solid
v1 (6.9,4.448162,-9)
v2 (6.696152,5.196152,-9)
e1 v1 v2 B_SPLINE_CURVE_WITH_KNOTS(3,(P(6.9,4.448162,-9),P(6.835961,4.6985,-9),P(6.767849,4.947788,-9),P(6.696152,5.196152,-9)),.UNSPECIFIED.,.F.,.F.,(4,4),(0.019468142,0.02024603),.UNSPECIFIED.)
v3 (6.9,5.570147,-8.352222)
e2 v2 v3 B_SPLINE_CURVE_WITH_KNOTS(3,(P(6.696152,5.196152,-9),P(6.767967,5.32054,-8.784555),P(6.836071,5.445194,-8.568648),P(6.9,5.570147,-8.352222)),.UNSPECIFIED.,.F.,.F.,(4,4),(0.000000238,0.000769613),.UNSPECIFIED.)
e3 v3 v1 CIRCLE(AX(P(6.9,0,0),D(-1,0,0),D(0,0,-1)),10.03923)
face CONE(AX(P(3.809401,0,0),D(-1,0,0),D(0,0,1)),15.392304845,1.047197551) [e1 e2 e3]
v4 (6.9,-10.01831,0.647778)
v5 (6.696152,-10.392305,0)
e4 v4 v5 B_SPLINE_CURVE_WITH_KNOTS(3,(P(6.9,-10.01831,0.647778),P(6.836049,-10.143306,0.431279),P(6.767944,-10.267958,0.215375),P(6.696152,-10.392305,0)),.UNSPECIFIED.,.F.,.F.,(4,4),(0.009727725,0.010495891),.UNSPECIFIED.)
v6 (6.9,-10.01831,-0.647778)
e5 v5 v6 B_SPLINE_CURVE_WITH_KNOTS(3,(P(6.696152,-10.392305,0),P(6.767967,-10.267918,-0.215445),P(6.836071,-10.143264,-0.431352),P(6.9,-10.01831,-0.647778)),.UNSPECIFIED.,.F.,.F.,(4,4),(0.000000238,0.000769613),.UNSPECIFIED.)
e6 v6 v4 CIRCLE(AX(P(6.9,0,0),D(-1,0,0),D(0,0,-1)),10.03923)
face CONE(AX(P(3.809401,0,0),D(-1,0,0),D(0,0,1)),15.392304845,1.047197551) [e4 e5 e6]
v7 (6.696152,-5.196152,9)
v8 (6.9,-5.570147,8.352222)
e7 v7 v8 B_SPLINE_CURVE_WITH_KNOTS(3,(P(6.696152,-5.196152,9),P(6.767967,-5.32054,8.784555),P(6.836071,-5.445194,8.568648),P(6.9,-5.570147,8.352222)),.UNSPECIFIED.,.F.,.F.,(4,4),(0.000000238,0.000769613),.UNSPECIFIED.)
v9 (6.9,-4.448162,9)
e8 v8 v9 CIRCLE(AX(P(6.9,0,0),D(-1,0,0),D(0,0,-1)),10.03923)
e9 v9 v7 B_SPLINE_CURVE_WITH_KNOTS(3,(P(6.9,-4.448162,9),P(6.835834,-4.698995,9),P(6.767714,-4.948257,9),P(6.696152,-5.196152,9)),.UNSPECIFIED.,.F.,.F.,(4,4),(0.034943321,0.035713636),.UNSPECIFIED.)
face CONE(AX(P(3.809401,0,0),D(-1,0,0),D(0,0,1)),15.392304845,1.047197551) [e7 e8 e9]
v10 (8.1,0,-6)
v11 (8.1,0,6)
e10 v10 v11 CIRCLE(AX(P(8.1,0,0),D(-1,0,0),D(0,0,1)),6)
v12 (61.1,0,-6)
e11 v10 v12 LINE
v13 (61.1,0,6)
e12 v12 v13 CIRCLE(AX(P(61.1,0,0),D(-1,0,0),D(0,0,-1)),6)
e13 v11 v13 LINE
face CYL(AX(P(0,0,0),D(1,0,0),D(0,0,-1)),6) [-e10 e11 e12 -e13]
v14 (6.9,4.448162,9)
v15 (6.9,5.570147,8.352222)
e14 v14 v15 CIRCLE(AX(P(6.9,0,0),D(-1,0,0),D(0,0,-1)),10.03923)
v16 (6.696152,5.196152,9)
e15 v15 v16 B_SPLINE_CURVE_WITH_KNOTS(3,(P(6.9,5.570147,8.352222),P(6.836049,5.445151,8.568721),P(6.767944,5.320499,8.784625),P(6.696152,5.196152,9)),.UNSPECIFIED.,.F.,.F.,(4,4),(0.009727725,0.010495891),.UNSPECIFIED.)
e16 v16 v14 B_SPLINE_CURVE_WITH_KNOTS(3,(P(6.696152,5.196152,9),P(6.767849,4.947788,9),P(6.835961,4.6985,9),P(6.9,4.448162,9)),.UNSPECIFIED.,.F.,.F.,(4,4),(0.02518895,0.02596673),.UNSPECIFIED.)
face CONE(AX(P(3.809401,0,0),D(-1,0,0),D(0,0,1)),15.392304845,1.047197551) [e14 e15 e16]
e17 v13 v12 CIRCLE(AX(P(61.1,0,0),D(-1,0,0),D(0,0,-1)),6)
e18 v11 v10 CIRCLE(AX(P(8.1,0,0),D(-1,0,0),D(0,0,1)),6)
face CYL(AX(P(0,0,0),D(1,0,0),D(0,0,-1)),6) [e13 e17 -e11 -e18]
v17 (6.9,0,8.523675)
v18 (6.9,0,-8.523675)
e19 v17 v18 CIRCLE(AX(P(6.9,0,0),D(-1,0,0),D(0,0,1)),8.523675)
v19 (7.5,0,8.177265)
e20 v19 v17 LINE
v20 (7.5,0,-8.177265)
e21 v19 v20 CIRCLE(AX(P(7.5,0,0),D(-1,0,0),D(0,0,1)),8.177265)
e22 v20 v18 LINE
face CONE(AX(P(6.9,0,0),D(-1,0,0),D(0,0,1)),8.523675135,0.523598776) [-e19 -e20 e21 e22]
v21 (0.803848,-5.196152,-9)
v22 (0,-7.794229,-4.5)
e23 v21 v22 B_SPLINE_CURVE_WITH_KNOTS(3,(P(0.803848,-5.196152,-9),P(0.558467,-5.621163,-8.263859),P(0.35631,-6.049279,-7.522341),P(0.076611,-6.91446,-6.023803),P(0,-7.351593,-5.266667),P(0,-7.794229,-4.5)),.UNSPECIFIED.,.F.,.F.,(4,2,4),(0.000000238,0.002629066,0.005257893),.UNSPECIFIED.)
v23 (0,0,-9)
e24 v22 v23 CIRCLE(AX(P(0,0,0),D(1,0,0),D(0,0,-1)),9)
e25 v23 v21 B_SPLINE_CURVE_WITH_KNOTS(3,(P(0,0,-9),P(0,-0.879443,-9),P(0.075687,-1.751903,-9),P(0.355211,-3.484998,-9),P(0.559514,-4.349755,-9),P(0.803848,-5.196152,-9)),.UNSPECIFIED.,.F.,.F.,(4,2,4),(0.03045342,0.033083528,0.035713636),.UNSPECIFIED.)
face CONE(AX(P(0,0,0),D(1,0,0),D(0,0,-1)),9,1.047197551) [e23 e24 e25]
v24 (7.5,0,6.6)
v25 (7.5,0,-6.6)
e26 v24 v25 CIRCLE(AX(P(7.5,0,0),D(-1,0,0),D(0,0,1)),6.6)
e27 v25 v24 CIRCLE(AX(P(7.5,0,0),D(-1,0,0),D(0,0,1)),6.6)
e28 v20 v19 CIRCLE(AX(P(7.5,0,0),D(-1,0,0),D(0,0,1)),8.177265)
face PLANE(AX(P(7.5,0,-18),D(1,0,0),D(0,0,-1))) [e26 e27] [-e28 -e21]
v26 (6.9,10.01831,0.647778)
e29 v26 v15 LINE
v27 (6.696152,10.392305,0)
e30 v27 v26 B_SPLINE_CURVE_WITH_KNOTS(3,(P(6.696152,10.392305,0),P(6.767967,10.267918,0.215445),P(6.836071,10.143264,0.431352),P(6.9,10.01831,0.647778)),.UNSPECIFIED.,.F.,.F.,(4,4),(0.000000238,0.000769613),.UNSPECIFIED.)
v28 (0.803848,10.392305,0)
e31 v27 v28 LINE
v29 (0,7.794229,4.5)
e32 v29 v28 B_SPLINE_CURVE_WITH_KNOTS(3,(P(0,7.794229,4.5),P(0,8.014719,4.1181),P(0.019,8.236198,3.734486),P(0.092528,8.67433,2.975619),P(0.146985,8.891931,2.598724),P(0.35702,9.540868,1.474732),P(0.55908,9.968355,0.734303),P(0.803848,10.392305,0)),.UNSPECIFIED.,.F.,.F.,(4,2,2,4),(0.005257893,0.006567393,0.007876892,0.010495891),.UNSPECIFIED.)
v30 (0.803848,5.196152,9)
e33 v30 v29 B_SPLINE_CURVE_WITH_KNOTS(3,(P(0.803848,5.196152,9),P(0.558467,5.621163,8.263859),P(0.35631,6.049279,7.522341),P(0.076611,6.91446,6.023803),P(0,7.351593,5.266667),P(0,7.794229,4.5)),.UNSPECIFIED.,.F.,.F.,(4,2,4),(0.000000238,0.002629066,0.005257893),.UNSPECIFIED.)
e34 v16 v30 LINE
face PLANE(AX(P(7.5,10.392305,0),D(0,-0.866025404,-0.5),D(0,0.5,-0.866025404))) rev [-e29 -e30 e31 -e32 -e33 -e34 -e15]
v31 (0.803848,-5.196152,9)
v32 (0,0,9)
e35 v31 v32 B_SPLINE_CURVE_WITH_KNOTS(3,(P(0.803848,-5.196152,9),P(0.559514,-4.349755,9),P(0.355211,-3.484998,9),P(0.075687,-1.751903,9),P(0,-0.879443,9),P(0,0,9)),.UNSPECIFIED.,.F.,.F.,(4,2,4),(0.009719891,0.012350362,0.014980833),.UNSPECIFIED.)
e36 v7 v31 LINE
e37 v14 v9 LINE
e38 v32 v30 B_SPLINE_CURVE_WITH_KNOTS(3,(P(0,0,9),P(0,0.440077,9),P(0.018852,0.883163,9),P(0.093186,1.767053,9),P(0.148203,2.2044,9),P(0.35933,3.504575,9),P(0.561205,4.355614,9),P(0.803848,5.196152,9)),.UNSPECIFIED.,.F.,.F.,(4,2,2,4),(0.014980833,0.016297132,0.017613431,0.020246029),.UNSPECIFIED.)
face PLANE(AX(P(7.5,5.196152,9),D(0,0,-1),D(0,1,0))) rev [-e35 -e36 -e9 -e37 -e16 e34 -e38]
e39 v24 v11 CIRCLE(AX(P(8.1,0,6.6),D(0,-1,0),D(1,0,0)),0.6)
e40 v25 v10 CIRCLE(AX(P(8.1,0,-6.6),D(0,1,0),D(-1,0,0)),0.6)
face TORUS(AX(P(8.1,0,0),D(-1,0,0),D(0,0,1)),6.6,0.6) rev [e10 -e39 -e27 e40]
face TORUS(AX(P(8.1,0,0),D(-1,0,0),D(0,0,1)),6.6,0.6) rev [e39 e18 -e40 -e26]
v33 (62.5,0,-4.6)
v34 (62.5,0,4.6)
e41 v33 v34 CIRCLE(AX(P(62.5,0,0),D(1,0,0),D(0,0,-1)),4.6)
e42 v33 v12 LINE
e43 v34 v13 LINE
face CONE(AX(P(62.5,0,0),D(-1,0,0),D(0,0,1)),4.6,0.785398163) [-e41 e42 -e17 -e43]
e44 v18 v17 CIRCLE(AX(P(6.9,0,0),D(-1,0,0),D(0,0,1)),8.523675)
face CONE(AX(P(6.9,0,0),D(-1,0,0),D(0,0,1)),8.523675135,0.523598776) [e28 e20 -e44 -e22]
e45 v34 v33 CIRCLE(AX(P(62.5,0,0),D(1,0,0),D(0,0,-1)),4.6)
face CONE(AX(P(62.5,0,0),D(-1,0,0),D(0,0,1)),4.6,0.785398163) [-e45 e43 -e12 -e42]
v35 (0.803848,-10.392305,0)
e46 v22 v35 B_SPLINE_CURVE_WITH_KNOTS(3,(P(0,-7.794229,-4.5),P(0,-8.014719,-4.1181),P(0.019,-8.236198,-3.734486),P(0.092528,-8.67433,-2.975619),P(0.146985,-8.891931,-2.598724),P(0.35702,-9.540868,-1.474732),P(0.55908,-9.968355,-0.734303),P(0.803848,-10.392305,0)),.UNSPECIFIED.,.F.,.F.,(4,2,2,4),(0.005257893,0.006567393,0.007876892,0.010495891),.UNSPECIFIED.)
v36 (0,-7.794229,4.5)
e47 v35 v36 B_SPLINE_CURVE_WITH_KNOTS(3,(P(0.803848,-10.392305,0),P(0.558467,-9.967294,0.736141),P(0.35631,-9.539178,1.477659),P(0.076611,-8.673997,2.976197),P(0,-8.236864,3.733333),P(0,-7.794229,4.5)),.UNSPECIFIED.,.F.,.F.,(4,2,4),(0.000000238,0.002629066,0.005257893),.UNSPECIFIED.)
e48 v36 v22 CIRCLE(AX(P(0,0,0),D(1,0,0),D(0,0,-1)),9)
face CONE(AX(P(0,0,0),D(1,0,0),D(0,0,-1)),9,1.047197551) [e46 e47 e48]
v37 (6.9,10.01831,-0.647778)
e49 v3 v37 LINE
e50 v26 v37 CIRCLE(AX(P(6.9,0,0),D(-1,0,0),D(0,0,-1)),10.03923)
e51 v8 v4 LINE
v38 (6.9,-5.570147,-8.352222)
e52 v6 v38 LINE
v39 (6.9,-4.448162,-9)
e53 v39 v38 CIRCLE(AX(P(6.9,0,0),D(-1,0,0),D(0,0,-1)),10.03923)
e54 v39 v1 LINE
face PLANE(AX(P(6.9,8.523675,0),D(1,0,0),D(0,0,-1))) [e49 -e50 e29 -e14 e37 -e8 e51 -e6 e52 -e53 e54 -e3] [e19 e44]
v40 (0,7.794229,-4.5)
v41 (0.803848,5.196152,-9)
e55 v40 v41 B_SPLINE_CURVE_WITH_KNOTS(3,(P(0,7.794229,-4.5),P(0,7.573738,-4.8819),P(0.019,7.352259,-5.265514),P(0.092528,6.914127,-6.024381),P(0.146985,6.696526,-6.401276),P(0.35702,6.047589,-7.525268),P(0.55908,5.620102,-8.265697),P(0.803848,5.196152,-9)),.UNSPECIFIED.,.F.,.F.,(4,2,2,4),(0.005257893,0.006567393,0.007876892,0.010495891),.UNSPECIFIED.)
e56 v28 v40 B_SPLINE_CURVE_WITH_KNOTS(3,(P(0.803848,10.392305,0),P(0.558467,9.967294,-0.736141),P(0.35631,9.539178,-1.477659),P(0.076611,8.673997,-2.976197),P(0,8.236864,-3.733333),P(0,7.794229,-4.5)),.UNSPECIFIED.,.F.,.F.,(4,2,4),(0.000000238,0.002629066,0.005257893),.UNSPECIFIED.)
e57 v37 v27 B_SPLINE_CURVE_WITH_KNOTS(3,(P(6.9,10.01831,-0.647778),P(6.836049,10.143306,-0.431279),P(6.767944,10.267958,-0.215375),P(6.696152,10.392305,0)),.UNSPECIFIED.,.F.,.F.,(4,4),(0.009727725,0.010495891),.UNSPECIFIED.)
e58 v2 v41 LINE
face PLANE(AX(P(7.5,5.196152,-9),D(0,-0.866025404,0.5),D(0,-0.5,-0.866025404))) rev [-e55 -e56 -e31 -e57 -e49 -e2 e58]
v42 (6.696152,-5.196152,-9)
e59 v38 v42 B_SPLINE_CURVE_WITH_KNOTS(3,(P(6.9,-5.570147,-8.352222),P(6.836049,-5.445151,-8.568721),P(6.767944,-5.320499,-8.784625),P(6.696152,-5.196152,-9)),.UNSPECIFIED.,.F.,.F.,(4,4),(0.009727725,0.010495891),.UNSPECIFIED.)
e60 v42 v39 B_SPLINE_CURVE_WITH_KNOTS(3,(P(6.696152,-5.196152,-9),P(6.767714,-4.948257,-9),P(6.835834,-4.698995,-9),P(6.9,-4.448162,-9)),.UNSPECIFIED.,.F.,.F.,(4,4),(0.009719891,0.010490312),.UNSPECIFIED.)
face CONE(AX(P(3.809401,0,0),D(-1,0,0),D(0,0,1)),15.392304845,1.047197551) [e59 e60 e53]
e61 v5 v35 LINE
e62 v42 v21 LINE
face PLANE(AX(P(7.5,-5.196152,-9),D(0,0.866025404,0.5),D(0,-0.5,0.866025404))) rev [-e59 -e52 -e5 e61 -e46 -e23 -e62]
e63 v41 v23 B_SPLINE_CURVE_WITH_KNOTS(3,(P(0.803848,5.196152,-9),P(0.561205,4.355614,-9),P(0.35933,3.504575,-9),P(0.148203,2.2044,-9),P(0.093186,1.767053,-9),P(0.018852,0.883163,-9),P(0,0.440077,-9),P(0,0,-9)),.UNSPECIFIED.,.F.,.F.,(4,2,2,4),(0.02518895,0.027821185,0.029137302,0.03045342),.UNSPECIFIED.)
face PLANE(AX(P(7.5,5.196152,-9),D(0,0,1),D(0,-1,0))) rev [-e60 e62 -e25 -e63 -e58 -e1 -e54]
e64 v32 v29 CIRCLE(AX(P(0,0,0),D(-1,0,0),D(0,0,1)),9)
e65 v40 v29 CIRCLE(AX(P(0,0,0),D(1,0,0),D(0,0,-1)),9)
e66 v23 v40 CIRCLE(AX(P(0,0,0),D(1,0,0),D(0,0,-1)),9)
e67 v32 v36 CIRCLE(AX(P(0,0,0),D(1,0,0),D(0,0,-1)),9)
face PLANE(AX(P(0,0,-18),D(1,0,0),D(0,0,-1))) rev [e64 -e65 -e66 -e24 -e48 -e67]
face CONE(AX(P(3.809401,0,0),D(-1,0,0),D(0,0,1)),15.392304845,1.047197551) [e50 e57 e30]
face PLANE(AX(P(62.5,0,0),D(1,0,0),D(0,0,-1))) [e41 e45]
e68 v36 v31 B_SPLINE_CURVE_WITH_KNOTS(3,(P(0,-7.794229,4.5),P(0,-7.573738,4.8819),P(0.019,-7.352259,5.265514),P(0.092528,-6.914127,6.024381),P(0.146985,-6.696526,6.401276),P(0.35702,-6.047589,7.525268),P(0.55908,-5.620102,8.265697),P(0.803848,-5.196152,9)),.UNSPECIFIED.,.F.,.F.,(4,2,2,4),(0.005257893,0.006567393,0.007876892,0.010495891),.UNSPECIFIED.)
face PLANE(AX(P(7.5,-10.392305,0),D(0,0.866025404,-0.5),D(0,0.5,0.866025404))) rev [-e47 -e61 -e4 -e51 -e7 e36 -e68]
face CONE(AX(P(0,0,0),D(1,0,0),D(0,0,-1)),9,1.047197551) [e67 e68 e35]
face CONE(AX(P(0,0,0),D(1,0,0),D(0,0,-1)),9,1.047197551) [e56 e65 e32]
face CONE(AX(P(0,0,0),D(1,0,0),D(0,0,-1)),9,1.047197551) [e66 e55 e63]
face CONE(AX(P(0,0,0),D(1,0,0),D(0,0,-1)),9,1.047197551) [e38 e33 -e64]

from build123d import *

# Parameters (mm, degrees)
BOSS_EXTRUDE_DEPTH = 7.5
CHAMFER_2_SIZE     = 1.4


with BuildPart() as part:
    # Sketch1 → Boss-Extrude (new body)
    with BuildSketch(Plane(origin=(0, 0, 0), x_dir=(0, 0, -1), z_dir=(1, 0, 0))):
        Polygon((9, 5.196152423), (9, -5.196152423), (0, -10.392304845), (-9, -5.196152423), (-9, 5.196152423), (0, 10.392304845), align=None)
    extrude(amount=BOSS_EXTRUDE_DEPTH)

    # Sketch2 → Boss-Revolve1 (revolve)
    with BuildSketch(Plane.XY, mode=Mode.PRIVATE) as boss_revolve1_sk:
        Polygon((0, 0), (62.5, 0), (62.5, 4.4845), (62.5, 6), (7.5, 6), (0, 6), align=None)
    revolve(boss_revolve1_sk.sketch.rotate(Axis((0, 0, 0), (-1, 0, 0)), 90), axis=Axis((0, 0, 0), (-1, 0, 0)))

    # Sketch3 → Cut-Revolve1 (revolve, cut)
    with BuildSketch(Plane.XY):
        Polygon((0, 9), (3.690598923, 15.392304845), (3.690598923, 20.392304845), (-10, 20.392304845), (-10, 9), align=None)
    revolve(axis=Axis((0, 0, 0), (1, 0, 0)), mode=Mode.SUBTRACT)

    # Sketch5 → Cut-Revolve2 (revolve, cut)
    with BuildSketch(Plane.XY):
        Polygon((7.5, 9), (3.809401077, 15.392304845), (3.809401077, 20.392304845), (13.809401077, 20.392304845), (13.809401077, 9), align=None)
    revolve(axis=Axis((0, 0, 0), (1, 0, 0)), mode=Mode.SUBTRACT)

    # Sketch4 → Cut-Revolve3 (revolve, cut)
    with BuildSketch(Plane.XY, mode=Mode.PRIVATE) as cut_revolve3_sk:
        Polygon((7.5, 8.177264973), (6.9, 8.523675135), (6.9, 20.392304845), (7.5, 20.392304845), align=None)
    revolve(cut_revolve3_sk.sketch.rotate(Axis((0, 0, 0), (1, 0, 0)), 90), axis=Axis((0, 0, 0), (1, 0, 0)), mode=Mode.SUBTRACT)

    # Chamfer 2
    chamfer_2_edges = [part.edges().sort_by_distance(p)[0] for p in [
        (62.5, 0, 6),
    ]]
    chamfer(chamfer_2_edges, length=CHAMFER_2_SIZE)

    # Sketch9 → Revolve1 (revolve)
    with BuildSketch(Plane.XY, mode=Mode.PRIVATE) as revolve1_sk:
        with BuildLine():
            Line((7.5, 6.6), (7.5, 6))
            Line((7.5, 6), (8.1, 6))
            ThreePointArc((8.1, 6), (7.675735931, 6.175735931), (7.5, 6.6))
        make_face()
    revolve(revolve1_sk.sketch.rotate(Axis((0, 0, 0), (1, 0, 0)), 90), axis=Axis((0, 0, 0), (1, 0, 0)))


solid = part.part
